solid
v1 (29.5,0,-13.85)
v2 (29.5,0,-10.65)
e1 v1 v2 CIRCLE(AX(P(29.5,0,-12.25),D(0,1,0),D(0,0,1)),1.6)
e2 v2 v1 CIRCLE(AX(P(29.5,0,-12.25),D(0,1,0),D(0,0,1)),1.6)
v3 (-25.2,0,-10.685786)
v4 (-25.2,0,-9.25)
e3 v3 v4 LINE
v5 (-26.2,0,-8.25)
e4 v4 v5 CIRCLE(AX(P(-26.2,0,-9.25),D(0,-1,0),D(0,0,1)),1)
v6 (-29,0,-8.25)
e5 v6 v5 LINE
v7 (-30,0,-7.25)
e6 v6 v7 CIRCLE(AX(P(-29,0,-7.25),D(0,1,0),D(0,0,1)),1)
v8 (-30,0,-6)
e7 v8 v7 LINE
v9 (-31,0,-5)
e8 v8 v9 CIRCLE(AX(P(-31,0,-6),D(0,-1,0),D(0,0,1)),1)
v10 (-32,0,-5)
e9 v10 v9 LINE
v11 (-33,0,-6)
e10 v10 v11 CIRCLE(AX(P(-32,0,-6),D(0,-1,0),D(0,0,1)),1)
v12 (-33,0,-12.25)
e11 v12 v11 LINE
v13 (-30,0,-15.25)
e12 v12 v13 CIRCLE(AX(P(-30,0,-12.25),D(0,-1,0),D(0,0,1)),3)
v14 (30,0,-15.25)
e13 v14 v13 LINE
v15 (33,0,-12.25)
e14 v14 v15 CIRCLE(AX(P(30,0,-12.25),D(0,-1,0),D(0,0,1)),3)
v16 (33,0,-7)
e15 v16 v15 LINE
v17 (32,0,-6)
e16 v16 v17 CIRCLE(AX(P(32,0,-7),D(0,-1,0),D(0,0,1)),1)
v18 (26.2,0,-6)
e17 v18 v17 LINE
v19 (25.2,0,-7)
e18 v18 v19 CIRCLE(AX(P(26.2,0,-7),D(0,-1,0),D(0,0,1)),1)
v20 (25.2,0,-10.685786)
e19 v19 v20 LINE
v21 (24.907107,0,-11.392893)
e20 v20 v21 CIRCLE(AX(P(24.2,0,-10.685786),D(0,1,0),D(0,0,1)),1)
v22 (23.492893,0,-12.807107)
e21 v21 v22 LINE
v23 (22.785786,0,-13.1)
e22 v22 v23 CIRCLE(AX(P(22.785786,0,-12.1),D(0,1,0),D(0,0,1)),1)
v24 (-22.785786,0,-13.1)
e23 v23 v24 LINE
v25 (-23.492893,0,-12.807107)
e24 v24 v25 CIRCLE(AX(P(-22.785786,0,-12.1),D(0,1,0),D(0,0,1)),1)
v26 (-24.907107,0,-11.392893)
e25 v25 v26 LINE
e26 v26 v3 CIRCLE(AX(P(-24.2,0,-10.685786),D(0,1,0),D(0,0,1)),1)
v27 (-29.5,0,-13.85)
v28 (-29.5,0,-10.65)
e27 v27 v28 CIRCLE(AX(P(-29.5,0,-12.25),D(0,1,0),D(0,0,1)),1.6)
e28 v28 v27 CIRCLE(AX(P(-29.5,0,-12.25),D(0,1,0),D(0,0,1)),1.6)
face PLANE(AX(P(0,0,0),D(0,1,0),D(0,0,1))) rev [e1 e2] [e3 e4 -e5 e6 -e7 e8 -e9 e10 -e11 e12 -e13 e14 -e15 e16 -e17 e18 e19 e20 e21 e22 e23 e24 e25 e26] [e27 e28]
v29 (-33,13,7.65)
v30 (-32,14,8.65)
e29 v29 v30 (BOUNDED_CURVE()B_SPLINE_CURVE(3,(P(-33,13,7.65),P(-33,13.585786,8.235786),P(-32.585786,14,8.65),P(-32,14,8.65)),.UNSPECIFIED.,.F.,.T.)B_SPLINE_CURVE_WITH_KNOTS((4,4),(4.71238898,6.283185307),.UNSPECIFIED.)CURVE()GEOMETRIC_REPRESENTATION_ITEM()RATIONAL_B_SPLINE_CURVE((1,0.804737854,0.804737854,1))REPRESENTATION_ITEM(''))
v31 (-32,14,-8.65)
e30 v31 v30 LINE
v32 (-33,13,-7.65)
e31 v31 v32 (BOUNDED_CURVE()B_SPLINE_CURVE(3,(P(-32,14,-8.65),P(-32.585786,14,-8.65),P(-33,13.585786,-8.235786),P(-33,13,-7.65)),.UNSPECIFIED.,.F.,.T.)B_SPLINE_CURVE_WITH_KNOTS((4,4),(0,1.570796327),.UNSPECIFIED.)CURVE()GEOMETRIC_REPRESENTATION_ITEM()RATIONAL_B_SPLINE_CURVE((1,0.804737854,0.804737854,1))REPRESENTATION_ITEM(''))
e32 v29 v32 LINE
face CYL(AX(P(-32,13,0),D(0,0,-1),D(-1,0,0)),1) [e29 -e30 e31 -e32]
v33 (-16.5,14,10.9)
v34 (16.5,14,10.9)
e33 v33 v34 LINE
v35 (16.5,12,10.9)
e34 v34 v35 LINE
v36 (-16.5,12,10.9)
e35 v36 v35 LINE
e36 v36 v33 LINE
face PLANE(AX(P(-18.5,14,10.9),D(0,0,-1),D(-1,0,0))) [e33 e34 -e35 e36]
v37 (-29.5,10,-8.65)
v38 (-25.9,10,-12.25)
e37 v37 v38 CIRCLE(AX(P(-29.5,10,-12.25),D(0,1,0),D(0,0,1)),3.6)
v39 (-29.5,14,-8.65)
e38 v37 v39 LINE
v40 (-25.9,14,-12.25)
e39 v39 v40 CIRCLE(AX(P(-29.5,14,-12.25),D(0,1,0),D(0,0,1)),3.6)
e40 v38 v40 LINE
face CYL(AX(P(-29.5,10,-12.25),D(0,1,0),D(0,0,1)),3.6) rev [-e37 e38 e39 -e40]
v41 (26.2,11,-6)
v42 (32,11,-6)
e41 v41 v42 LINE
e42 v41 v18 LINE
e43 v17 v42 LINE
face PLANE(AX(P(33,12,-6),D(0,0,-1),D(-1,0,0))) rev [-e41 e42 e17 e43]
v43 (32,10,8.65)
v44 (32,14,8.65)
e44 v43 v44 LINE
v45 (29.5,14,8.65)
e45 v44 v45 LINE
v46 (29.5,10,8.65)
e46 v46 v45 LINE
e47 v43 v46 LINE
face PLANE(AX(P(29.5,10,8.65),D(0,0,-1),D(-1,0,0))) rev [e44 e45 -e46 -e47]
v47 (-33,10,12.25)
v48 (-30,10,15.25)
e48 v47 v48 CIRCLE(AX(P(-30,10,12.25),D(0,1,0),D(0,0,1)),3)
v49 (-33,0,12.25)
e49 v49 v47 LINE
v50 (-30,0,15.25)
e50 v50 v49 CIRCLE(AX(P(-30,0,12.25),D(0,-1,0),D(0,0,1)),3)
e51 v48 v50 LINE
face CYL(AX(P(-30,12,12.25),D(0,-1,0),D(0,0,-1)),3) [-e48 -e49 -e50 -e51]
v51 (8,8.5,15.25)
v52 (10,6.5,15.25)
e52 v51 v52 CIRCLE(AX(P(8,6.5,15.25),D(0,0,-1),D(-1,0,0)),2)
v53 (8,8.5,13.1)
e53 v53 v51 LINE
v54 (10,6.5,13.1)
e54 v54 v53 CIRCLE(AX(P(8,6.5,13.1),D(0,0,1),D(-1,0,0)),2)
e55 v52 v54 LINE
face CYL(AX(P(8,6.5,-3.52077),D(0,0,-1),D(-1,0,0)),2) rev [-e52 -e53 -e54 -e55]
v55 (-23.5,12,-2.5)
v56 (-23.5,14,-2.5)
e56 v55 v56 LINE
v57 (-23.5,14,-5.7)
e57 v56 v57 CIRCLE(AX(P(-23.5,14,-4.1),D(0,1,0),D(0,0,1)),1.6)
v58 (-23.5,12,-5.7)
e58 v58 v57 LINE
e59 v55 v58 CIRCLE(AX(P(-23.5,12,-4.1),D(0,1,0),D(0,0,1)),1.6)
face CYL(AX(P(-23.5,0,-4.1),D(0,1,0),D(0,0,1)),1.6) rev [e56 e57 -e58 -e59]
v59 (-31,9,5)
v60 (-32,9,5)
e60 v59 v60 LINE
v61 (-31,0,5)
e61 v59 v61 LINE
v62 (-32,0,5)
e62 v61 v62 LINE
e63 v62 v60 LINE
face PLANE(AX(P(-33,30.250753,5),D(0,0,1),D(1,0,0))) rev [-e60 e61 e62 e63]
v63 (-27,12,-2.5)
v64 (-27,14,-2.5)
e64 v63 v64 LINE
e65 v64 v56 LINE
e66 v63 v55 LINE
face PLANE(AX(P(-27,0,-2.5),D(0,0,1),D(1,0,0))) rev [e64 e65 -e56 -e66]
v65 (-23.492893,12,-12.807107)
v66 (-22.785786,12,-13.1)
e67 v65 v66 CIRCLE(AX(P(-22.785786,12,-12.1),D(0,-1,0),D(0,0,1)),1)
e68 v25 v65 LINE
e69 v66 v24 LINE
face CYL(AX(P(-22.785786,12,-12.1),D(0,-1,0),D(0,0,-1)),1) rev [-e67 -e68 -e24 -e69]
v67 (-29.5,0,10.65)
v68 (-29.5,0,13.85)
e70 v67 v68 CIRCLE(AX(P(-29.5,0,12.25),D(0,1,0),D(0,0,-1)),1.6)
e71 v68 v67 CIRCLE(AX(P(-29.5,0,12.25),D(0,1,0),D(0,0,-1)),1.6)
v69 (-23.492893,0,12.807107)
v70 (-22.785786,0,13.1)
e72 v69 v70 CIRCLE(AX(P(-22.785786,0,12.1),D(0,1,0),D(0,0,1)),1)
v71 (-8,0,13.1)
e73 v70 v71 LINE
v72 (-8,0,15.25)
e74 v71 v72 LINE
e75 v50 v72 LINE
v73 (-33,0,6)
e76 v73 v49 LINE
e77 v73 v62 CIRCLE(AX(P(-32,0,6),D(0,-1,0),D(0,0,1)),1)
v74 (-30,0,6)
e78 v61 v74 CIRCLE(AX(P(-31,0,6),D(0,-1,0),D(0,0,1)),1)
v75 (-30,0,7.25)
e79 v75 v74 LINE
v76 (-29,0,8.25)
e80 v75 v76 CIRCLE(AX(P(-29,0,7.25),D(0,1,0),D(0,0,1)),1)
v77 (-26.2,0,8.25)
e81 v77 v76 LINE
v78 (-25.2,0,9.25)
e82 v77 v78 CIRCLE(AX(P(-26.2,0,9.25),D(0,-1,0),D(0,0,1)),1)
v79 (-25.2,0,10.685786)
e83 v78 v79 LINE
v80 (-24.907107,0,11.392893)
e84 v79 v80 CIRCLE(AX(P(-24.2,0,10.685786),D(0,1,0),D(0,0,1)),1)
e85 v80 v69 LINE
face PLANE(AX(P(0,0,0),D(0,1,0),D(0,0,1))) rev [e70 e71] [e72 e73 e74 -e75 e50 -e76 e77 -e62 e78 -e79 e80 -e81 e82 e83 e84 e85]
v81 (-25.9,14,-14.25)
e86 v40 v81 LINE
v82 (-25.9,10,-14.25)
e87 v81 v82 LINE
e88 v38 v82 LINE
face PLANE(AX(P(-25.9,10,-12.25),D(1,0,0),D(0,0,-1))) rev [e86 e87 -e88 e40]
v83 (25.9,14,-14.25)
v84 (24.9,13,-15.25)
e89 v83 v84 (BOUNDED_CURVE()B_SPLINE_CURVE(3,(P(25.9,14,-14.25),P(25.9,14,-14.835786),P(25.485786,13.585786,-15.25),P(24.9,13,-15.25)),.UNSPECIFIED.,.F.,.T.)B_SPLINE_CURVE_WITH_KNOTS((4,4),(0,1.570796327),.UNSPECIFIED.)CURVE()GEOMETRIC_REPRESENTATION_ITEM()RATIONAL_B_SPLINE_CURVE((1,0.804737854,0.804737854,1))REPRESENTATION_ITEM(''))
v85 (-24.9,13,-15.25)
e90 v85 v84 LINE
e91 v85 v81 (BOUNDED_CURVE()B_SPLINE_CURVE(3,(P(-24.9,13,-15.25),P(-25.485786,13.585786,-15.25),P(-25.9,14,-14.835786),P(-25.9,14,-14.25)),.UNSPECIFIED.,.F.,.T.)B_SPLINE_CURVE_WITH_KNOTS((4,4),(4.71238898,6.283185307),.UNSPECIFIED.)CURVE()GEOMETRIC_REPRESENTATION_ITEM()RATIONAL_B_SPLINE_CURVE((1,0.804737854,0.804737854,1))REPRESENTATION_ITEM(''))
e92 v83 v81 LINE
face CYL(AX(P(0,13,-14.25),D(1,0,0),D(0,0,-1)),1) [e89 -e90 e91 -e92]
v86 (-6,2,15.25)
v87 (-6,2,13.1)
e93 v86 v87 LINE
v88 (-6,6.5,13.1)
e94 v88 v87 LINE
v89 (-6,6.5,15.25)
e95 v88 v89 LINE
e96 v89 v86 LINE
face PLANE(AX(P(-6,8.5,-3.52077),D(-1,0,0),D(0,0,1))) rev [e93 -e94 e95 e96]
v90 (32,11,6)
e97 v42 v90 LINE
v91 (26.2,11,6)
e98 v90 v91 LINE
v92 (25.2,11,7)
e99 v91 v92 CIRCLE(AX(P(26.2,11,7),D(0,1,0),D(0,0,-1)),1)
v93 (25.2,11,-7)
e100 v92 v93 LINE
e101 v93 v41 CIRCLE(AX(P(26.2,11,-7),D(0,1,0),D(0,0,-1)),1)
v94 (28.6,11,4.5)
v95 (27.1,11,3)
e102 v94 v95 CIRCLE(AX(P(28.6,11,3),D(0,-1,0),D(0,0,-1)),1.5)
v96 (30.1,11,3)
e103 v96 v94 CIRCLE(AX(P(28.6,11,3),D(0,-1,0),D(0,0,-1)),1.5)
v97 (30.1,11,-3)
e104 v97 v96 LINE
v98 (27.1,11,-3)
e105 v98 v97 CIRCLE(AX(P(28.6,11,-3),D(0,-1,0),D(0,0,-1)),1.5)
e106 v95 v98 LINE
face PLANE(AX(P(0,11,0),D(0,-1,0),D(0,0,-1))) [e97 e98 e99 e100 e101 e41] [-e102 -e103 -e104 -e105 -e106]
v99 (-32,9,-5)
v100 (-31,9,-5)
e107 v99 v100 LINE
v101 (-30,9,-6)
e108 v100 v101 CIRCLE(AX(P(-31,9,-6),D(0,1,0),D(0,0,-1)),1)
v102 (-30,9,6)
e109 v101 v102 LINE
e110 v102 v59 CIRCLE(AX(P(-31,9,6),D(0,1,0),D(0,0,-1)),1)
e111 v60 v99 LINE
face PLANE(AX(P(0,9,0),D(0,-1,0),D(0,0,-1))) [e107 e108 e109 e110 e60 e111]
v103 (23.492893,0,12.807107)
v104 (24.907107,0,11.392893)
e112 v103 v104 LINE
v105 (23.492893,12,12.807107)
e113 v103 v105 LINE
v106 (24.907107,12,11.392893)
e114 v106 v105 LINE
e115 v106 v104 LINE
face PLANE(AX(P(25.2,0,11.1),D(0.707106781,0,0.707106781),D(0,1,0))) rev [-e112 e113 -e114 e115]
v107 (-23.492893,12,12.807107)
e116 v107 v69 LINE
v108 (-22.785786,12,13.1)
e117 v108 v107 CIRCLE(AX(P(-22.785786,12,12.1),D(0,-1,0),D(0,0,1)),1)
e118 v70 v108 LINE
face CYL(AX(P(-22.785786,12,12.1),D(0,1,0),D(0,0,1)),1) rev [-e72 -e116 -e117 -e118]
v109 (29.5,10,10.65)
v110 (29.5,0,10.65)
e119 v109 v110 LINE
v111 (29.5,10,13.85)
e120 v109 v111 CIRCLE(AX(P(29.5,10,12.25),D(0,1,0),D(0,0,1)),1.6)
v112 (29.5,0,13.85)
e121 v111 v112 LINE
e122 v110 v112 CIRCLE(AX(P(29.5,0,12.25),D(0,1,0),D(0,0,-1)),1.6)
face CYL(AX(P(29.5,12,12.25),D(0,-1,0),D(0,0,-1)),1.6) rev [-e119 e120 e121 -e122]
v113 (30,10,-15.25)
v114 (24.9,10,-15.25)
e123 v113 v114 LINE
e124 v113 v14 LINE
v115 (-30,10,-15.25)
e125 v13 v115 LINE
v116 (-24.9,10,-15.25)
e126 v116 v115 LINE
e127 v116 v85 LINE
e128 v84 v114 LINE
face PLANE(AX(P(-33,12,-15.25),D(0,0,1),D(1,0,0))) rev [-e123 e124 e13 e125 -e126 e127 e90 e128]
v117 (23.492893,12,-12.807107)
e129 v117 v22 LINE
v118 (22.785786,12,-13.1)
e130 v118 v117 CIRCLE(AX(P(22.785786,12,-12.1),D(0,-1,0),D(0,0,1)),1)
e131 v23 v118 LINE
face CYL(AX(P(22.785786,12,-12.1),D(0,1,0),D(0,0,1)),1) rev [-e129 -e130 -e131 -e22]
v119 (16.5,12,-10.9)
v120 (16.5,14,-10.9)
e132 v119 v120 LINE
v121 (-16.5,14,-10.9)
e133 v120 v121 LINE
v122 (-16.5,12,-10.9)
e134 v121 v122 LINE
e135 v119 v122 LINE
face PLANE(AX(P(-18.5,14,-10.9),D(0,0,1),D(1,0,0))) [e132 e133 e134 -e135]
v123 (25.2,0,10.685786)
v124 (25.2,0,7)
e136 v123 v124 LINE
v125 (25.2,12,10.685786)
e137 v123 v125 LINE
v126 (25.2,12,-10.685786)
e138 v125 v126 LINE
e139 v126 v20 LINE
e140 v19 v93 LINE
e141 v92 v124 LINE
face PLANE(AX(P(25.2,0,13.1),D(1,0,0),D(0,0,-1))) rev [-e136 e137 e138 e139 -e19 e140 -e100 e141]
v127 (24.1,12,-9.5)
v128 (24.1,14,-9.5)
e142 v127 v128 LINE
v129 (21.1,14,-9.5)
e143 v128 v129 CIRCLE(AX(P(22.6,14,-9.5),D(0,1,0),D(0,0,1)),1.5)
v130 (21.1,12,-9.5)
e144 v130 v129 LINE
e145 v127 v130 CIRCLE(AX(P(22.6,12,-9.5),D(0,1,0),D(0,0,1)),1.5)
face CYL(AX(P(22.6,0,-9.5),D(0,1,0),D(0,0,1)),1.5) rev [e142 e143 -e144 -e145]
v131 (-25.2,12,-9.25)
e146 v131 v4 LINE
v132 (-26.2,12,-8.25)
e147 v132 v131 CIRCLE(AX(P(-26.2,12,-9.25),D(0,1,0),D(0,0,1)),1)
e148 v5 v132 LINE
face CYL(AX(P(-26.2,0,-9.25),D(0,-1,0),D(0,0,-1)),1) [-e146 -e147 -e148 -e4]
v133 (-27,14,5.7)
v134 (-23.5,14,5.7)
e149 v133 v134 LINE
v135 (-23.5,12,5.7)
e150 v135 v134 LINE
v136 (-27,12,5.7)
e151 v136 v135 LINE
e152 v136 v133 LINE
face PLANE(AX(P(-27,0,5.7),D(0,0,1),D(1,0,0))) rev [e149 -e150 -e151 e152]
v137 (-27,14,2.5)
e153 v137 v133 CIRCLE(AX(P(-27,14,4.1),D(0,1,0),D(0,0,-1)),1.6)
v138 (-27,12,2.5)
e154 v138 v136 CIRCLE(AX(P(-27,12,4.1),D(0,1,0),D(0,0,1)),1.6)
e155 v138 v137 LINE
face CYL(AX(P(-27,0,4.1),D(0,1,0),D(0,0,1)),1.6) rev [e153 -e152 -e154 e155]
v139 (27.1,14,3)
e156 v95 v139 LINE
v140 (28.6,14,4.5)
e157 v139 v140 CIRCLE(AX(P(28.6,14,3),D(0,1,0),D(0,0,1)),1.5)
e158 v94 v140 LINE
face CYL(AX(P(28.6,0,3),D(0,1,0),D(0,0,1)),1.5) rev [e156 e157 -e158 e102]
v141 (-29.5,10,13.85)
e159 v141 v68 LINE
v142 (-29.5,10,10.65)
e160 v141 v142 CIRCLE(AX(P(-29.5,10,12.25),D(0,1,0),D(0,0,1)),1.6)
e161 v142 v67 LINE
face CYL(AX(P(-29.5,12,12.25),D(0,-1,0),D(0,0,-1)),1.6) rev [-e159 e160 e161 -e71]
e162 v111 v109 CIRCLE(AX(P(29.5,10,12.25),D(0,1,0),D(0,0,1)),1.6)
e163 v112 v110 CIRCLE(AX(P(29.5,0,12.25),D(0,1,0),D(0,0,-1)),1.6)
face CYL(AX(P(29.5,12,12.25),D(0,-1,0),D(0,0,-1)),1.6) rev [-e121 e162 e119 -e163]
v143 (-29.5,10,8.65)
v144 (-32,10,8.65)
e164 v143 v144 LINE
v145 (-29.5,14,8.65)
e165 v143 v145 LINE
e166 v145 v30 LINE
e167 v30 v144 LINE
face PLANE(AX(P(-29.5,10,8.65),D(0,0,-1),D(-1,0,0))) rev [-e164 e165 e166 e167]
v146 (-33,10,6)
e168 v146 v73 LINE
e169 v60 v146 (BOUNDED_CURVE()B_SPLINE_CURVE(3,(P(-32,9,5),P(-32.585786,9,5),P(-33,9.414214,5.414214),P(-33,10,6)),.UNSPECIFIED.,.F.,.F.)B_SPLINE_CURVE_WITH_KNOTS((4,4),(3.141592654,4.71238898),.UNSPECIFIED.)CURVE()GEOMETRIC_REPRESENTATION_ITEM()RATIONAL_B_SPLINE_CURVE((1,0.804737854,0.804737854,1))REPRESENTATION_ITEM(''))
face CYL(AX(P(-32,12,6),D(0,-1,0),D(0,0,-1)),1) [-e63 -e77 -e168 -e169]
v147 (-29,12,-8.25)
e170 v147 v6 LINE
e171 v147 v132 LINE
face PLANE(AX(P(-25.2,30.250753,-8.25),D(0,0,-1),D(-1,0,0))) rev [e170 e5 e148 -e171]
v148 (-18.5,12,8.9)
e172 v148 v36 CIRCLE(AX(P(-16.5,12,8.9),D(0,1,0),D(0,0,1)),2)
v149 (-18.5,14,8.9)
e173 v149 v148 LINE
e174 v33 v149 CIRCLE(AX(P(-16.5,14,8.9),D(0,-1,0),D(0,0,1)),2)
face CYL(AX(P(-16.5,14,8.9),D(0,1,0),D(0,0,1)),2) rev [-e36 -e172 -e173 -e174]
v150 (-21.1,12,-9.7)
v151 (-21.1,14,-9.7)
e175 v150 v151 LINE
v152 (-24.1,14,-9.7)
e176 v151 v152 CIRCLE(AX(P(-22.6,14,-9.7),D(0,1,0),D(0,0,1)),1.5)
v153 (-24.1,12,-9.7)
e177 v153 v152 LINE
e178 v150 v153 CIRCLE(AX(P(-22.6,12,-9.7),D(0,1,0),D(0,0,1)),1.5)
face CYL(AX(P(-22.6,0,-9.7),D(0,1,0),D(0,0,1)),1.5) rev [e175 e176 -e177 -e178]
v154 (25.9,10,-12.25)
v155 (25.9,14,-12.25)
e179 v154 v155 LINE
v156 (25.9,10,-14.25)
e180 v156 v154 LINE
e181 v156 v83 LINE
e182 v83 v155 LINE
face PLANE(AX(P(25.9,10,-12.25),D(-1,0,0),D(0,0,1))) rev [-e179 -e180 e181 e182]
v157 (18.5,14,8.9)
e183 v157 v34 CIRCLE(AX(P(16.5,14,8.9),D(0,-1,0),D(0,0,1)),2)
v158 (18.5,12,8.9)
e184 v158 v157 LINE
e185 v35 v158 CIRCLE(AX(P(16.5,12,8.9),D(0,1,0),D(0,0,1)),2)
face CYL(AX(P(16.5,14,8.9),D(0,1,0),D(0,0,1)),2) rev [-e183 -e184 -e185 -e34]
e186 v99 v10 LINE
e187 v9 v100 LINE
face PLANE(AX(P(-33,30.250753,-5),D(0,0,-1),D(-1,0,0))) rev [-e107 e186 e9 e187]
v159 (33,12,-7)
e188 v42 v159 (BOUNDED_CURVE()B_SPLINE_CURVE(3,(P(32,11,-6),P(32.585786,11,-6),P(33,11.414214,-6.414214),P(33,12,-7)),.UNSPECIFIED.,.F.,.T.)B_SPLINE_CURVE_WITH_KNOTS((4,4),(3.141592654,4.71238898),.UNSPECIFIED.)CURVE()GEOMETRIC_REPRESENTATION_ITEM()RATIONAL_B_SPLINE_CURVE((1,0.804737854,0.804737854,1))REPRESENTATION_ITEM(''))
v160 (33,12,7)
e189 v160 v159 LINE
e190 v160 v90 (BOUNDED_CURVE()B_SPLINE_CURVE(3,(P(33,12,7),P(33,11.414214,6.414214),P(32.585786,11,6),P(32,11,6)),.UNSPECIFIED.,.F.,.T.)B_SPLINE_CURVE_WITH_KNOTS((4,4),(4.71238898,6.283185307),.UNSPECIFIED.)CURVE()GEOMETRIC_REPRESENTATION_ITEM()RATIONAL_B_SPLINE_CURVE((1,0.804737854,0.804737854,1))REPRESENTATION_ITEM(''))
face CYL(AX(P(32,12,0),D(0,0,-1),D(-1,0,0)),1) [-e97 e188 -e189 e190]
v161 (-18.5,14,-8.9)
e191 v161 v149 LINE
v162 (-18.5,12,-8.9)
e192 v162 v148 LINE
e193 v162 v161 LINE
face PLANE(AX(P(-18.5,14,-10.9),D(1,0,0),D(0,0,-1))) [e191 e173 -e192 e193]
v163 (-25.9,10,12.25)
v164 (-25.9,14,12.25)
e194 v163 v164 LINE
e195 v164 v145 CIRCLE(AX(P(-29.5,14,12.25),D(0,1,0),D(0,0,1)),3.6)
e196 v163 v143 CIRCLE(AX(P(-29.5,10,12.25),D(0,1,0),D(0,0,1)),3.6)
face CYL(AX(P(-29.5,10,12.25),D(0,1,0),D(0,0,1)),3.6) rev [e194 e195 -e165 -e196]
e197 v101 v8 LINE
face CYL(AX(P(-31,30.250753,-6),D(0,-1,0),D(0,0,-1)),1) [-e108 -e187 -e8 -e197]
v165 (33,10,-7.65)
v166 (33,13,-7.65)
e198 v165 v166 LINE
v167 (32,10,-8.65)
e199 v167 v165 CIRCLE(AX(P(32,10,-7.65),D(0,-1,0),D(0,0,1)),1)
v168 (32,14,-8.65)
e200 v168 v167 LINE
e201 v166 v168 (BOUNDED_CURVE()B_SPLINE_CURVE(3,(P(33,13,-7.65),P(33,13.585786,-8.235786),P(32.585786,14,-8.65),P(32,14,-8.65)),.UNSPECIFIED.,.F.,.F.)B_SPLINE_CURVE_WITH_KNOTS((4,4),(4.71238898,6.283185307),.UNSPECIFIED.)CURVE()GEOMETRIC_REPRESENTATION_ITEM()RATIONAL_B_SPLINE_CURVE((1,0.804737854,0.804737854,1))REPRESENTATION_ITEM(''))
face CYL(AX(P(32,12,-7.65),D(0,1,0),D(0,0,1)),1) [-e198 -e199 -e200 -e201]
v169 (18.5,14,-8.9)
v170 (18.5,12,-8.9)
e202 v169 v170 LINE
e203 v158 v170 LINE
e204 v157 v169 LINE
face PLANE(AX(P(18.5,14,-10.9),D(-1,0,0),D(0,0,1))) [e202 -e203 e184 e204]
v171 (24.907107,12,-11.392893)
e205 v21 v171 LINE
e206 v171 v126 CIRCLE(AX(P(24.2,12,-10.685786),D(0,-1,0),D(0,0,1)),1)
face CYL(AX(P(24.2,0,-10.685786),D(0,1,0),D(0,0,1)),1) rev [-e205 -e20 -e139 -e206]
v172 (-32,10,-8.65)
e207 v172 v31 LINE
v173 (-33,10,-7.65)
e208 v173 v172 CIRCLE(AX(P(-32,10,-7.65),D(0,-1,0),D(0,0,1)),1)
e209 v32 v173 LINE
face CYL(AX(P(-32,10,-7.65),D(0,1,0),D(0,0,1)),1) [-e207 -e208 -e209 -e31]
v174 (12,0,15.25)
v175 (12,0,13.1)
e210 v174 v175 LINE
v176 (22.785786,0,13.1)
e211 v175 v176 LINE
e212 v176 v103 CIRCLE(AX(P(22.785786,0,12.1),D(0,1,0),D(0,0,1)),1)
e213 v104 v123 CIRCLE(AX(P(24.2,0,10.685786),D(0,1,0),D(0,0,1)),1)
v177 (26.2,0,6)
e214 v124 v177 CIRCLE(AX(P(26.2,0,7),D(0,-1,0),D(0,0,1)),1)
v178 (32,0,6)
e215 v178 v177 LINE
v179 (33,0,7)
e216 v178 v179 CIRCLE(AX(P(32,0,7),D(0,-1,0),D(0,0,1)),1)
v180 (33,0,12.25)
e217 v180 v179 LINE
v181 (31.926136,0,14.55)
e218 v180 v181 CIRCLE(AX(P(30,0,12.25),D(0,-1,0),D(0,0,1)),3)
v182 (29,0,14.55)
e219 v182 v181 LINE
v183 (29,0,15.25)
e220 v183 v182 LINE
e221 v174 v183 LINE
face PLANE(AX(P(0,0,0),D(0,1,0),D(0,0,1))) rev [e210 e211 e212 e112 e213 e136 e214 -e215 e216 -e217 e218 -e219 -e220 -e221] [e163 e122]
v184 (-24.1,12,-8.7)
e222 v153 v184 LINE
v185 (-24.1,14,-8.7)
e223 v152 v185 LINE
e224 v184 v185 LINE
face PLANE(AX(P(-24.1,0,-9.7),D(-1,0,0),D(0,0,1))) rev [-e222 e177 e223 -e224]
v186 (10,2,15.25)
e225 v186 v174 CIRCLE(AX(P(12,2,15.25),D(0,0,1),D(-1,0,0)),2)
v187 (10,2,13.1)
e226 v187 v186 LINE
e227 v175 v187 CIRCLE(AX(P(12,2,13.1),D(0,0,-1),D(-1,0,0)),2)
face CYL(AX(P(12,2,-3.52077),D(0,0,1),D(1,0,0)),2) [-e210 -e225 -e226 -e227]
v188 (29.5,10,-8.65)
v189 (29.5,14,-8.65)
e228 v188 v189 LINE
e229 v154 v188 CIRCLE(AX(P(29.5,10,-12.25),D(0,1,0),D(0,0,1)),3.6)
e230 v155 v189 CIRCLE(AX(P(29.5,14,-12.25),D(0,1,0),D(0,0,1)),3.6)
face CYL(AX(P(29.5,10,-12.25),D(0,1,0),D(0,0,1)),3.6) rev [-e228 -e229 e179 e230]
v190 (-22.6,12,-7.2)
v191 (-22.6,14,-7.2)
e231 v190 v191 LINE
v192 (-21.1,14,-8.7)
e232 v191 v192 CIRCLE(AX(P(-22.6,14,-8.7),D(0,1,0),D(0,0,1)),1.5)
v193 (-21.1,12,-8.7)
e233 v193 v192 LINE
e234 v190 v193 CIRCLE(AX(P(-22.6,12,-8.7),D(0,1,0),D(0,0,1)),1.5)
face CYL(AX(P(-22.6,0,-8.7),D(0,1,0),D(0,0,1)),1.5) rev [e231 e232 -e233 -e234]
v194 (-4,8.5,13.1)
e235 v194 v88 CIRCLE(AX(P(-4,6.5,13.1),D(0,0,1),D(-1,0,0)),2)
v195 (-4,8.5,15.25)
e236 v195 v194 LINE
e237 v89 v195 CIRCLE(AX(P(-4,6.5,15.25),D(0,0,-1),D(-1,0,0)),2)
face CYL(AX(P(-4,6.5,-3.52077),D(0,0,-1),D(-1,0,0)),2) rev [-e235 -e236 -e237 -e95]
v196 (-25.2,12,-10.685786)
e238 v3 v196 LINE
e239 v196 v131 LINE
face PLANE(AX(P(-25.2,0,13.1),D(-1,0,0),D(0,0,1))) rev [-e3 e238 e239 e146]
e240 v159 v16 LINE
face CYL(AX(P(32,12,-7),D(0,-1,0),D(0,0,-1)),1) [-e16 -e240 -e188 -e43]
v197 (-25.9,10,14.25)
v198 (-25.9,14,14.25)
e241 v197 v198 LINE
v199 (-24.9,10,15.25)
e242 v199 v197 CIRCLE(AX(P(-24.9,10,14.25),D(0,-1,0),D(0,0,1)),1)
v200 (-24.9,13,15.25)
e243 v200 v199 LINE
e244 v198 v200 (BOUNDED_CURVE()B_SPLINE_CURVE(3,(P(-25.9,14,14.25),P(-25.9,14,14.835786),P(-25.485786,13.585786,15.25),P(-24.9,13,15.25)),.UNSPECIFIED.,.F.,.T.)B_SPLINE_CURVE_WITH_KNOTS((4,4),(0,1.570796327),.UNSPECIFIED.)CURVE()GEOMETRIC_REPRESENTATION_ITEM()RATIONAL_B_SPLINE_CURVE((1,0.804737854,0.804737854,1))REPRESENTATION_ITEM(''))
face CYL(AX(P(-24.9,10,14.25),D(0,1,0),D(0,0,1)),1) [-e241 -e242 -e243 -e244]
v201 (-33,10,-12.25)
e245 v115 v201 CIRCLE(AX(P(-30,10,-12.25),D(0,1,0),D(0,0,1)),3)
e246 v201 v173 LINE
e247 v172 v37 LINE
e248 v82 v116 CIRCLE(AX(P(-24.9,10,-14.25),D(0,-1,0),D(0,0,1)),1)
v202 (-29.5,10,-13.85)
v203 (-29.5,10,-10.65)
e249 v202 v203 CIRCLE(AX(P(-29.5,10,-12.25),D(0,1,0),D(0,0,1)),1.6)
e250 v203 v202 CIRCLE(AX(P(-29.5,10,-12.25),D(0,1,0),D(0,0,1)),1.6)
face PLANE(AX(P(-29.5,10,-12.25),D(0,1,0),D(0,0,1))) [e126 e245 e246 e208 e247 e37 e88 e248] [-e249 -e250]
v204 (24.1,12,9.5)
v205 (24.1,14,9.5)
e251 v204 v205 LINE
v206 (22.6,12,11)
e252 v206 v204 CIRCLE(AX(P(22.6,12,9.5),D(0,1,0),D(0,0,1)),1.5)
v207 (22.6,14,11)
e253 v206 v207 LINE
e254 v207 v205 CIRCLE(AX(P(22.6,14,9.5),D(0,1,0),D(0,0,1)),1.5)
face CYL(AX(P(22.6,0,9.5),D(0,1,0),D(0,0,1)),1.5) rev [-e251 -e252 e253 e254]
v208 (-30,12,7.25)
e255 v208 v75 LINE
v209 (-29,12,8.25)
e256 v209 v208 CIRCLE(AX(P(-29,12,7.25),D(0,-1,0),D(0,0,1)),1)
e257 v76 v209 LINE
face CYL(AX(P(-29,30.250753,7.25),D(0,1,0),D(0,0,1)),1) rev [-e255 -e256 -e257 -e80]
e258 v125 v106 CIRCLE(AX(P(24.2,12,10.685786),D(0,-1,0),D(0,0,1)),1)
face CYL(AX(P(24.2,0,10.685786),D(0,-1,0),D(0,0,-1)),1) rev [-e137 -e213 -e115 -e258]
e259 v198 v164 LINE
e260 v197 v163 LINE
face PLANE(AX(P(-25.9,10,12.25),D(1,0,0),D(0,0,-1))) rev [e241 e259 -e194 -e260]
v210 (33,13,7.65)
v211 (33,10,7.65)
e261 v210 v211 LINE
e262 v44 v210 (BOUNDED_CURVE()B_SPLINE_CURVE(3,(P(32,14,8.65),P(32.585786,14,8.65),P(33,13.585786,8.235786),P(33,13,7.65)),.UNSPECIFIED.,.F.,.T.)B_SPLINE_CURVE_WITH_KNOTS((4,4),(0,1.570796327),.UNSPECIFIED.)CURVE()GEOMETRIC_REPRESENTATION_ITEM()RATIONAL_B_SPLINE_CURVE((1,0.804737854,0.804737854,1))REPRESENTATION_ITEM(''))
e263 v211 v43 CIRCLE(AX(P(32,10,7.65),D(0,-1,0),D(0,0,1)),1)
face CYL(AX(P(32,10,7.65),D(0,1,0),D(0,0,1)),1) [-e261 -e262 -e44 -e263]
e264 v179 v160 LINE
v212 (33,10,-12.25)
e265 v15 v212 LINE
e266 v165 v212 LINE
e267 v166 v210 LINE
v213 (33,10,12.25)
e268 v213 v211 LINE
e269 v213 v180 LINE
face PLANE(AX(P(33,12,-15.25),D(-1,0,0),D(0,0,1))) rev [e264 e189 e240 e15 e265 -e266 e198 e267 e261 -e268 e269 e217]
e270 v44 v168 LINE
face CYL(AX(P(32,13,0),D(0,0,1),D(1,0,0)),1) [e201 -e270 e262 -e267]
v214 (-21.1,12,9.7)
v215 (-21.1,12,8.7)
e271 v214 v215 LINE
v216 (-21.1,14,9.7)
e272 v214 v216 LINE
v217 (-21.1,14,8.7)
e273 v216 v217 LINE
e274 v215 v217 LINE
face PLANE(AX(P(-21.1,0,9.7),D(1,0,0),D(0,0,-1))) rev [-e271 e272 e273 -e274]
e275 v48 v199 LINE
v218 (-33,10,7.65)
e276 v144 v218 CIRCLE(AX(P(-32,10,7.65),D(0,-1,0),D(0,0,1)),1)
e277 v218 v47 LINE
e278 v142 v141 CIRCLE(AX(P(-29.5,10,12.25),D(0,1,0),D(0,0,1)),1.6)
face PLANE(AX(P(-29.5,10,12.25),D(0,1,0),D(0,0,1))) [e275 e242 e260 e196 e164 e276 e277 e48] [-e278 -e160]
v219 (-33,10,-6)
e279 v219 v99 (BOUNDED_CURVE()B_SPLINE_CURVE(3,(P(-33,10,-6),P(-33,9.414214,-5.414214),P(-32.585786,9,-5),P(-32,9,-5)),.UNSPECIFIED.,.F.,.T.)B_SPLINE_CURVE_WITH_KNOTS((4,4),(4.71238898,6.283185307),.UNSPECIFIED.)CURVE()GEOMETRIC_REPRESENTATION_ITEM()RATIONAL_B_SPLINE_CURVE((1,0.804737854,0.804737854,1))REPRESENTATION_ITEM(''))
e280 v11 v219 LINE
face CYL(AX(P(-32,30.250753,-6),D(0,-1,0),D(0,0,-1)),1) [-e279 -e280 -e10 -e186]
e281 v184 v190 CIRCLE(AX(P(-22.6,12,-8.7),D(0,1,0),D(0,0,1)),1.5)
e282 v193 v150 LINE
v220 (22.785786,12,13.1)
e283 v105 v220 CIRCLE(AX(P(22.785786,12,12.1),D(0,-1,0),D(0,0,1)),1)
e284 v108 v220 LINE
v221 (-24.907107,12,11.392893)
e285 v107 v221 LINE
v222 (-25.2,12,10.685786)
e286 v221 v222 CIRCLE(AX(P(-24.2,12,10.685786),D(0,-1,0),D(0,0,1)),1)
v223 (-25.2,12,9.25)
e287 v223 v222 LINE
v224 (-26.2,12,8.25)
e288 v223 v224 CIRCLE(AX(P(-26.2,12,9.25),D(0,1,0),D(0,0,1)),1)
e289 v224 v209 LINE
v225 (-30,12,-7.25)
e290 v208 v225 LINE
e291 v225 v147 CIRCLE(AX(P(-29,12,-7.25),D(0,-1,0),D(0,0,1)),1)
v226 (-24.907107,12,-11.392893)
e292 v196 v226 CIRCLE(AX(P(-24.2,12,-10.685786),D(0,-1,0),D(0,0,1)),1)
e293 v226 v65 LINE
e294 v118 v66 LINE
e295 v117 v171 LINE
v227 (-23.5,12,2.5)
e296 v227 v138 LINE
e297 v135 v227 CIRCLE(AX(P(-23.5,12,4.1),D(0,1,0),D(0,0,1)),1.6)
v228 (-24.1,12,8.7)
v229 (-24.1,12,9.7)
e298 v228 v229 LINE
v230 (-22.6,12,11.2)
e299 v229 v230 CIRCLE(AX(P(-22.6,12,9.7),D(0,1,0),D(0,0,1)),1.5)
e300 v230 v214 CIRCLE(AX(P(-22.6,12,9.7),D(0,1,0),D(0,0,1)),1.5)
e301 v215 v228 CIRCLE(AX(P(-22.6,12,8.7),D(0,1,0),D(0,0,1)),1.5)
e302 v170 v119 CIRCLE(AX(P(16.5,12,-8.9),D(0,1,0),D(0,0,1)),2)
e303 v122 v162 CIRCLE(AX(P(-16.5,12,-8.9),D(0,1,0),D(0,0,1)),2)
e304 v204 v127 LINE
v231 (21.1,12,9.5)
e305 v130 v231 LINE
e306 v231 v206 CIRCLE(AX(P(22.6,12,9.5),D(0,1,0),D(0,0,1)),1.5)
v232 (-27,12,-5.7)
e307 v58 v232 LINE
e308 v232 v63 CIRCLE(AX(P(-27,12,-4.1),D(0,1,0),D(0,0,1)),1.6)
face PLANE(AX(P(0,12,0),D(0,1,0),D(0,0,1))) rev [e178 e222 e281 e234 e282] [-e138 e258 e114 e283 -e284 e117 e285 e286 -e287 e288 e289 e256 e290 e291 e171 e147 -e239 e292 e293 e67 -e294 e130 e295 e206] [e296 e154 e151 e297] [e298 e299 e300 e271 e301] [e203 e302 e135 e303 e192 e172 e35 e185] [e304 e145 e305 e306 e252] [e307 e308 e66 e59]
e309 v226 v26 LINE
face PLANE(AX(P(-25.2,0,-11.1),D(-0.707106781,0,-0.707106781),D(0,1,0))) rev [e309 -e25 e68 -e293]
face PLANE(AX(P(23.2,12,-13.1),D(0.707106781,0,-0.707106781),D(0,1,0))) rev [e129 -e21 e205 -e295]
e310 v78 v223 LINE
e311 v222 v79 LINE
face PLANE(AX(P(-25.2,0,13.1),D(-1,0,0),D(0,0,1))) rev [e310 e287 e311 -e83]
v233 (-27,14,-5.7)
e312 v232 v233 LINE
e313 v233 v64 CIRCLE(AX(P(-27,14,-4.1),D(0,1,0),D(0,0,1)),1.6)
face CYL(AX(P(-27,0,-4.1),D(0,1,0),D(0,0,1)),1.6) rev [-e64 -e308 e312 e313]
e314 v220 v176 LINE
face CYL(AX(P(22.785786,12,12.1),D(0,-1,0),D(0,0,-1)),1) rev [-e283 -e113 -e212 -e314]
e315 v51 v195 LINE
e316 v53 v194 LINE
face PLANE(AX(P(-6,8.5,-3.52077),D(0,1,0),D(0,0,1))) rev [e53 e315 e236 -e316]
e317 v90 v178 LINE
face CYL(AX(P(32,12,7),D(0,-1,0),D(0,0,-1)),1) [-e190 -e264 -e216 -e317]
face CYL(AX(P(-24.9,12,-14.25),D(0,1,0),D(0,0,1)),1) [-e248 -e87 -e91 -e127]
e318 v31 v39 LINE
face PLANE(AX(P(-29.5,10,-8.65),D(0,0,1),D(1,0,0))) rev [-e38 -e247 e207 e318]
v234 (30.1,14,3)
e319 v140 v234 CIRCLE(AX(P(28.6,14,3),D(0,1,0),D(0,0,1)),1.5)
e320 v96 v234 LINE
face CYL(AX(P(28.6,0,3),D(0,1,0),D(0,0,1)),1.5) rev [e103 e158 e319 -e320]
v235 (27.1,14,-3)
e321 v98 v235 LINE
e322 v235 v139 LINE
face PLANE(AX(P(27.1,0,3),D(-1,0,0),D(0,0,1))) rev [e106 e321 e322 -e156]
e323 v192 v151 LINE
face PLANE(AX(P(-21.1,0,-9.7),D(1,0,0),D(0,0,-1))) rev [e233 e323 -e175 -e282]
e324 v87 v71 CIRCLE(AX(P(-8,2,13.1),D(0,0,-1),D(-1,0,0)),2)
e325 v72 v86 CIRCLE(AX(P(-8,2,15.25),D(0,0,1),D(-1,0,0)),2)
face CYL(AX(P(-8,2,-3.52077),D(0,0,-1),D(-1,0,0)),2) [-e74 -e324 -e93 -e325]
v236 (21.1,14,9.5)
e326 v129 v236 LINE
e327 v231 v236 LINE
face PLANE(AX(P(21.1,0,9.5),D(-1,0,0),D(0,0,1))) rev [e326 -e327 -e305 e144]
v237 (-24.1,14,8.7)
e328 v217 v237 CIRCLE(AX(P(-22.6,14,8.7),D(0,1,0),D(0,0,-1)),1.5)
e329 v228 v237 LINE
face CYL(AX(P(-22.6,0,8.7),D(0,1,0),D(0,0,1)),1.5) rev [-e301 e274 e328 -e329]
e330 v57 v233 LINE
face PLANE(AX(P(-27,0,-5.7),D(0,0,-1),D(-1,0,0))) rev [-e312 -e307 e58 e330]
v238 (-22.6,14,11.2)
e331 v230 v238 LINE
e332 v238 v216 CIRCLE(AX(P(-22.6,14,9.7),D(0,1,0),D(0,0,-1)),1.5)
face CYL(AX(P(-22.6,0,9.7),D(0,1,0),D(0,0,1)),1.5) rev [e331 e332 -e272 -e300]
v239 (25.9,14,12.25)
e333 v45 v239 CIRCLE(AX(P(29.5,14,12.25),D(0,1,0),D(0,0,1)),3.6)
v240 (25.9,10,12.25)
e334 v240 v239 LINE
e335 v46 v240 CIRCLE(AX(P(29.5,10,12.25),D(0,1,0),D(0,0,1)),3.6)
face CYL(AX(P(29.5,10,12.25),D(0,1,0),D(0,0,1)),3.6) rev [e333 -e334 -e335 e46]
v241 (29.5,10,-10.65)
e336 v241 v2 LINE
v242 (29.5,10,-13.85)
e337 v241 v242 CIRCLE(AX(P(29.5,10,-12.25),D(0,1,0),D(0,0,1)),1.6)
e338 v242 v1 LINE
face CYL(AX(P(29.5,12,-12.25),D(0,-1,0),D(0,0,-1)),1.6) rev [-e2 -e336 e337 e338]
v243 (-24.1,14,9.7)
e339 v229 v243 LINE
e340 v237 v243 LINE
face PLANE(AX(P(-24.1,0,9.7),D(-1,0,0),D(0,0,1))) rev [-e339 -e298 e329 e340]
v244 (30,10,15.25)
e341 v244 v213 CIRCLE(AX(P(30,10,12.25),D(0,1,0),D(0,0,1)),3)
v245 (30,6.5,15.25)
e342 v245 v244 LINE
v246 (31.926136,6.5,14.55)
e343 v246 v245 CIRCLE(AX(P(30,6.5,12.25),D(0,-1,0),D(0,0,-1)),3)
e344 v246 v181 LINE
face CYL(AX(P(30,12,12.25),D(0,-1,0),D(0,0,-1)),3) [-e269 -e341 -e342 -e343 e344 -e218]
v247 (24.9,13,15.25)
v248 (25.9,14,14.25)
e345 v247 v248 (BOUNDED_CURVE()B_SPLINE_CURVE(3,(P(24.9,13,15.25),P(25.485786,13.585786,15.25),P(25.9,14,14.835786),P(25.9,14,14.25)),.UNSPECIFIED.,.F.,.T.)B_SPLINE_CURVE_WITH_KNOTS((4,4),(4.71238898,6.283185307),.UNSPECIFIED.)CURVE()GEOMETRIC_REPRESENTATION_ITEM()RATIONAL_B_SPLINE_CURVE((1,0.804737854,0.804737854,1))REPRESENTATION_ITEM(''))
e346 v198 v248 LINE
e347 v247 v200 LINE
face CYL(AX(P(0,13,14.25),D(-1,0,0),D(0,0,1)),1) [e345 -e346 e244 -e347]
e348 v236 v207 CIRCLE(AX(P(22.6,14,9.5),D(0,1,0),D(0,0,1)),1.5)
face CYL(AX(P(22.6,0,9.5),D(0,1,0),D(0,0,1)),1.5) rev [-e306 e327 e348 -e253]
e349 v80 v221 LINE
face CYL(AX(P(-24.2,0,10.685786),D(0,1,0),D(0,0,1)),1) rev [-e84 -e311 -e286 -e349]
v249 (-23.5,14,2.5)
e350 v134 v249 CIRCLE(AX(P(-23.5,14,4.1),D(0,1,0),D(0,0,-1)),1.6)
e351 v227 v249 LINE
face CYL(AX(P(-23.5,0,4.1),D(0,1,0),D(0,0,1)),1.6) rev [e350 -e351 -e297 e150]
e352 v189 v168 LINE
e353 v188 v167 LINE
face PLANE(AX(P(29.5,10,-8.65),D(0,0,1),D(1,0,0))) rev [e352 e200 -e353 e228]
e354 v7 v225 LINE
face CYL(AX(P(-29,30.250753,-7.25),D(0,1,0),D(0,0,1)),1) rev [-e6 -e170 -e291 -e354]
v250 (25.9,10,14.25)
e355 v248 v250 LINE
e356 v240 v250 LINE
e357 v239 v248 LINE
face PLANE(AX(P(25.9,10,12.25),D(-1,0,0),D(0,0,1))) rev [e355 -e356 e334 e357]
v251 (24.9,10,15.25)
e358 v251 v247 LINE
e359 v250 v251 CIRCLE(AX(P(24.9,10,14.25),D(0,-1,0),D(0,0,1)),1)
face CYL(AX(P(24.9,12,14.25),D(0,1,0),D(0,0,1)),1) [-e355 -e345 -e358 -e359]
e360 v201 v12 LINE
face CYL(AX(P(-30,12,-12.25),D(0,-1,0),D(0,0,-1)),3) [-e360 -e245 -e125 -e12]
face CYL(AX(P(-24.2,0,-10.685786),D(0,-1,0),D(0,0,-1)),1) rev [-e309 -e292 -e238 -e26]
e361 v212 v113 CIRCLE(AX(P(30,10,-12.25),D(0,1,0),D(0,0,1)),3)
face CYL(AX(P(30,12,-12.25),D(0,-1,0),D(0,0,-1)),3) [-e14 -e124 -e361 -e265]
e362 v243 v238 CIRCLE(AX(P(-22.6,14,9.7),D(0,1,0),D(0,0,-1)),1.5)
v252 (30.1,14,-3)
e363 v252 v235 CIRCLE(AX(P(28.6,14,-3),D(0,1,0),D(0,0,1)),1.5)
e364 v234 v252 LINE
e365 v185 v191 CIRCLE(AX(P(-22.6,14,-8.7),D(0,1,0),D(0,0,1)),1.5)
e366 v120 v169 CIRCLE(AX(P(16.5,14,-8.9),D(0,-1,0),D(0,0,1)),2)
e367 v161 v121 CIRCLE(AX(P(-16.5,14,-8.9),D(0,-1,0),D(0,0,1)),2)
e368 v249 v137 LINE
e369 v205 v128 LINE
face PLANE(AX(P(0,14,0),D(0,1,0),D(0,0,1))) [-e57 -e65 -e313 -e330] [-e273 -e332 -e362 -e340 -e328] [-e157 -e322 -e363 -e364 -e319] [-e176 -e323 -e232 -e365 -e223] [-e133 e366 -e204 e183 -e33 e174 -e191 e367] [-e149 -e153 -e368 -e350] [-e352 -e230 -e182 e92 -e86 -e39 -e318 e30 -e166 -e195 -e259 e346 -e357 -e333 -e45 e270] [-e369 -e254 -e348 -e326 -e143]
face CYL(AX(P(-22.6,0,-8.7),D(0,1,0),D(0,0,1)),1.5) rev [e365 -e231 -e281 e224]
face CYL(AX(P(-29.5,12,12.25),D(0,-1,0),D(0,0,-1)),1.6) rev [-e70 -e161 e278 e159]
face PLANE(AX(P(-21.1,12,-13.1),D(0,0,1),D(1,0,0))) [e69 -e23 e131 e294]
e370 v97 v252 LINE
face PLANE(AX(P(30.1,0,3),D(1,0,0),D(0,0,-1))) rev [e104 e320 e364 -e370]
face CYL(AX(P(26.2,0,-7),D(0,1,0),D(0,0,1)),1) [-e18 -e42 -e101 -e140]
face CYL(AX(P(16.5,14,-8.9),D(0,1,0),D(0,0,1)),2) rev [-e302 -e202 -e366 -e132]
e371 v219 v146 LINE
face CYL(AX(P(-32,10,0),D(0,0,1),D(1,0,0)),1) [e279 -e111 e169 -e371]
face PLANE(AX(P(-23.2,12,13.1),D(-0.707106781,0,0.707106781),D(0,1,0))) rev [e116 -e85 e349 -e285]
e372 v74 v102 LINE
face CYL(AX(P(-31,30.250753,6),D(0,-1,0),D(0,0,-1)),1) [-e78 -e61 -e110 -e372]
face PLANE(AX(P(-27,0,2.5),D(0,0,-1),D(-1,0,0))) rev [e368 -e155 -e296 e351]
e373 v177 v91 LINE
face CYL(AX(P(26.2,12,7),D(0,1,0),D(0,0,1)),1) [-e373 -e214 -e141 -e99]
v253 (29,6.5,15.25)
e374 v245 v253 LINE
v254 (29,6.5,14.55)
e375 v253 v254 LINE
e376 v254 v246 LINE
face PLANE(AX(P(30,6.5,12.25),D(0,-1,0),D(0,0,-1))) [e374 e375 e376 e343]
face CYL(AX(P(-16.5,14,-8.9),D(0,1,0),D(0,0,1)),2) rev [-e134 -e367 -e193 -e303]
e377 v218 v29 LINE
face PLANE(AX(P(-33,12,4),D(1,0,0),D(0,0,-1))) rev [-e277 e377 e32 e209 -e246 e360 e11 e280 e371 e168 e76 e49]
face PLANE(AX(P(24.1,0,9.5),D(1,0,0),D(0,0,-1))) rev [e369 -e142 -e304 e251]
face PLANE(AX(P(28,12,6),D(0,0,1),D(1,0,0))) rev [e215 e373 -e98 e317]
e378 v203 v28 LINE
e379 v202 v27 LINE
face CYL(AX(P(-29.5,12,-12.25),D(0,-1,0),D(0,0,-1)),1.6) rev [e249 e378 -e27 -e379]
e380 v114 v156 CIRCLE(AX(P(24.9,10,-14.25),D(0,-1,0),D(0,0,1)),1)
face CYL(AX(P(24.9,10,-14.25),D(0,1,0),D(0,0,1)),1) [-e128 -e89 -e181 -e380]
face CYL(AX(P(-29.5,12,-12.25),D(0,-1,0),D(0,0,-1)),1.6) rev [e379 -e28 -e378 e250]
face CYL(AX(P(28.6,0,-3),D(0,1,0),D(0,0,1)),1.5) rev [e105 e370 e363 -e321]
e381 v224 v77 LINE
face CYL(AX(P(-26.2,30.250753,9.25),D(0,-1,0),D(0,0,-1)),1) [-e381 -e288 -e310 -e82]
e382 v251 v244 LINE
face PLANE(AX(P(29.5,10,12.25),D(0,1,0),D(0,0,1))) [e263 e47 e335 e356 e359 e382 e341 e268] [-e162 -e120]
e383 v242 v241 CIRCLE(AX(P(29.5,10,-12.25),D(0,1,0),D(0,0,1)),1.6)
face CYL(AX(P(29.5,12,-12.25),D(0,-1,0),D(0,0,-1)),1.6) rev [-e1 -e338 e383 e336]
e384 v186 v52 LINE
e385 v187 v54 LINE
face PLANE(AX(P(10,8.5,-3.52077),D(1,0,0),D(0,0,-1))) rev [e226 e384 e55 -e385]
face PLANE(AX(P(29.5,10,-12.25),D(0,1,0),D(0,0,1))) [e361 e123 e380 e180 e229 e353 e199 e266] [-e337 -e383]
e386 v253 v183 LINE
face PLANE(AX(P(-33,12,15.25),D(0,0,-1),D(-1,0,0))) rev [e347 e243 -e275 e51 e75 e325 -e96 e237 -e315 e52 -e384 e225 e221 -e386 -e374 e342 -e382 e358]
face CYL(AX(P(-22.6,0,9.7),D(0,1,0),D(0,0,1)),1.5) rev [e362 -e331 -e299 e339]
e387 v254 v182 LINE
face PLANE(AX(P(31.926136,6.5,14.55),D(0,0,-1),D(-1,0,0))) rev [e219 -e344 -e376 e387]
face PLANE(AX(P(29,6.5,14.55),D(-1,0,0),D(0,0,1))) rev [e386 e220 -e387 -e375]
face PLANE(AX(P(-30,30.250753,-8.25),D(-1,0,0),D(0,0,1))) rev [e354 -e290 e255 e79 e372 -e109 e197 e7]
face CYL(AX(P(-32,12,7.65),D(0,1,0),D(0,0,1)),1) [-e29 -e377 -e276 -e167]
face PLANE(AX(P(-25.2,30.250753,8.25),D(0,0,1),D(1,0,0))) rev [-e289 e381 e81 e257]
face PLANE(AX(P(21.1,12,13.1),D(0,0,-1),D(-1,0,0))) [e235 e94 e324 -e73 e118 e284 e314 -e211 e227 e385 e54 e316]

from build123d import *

# Parameters (mm, degrees)
SKETCH1_R              = 1.6
BOSS_EXTRUDE1_DEPTH    = 12
SKETCH2_W              = 52
SKETCH2_H              = 26.2
CUT_EXTRUDE1_DEPTH     = 2
SKETCH3_W              = 7.4
SKETCH3_H              = 20
CUT_EXTRUDE2_DEPTH     = 8
SKETCH4_W              = 16
SKETCH4_H              = 4.5
CUT_EXTRUDE3_DEPTH     = 2.15
SKETCH5_W              = 52
SKETCH5_H              = 26.2
CUT_EXTRUDE4_DEPTH     = 39.28266579
SKETCH6_W              = 66
SKETCH6_H              = 30.5
SKETCH6_R              = 1.6
SKETCH6_W_2            = 37
SKETCH6_H_2            = 21.8
BOSS_EXTRUDE2_DEPTH    = 2
SKETCH7_W              = 2
SKETCH7_H              = 12
SKETCH7_W_2            = 1.6
SKETCH7_H_2            = 8
CUT_EXTRUDE5_DEPTH     = 39.28266579
SKETCH8_W              = 16
SKETCH8_H              = 2.15
CUT_EXTRUDE6_DEPTH     = 38.33379836
SKETCH9_W              = 0.8
SKETCH9_H              = 7.1
BOSS_EXTRUDE3_DEPTH    = 12
CUT_EXTRUDE7_DEPTH     = 12
SKETCH11_W             = 3
SKETCH11_H             = 10
BOSS_EXTRUDE4_DEPTH    = 3
SKETCH13_W             = 7.8
SKETCH13_H             = 12
BOSS_EXTRUDE5_DEPTH    = 1
CHAMFER1_SIZE          = 2
CUT_EXTRUDE8_DEPTH     = 4
CUT_EXTRUDE9_DEPTH     = 39.955904559
R1_TRANSITION_FILLET_R = 1
R2_TRANSITION_FILLET_R = 2
R3_TRANSITION_FILLET_R = 3
CUT_EXTRUDE10_START    = -6.5
CUT_EXTRUDE10_DEPTH    = 6.5


with BuildPart() as part:
    # Sketch1 → Boss-Extrude1 (new body)
    with BuildSketch(Plane(origin=(0, 0, 0), x_dir=(1, 0, 0), z_dir=(0, 1, 0))):
        Polygon((-33, 4), (-27.6, 4), (-27.6, -4), (-33, -4), (-33, -15.25), (33, -15.25), (33, -6), (28, -6), (28, 6), (33, 6), (33, 15.25), (-33, 15.25), align=None)
        with Locations(Location((-29.5, 12.25, 0), (0, 0, 270))):
            Circle(SKETCH1_R, mode=Mode.SUBTRACT)
        with Locations(Location((29.5, 12.25, 0), (0, 0, 270))):
            Circle(SKETCH1_R, mode=Mode.SUBTRACT)
        with Locations(Location((-29.5, -12.25, 0), (0, 0, 90))):
            Circle(SKETCH1_R, mode=Mode.SUBTRACT)
        with Locations(Location((29.5, -12.25, 0), (0, 0, 90))):
            Circle(SKETCH1_R, mode=Mode.SUBTRACT)
        Polygon((-26, -5.75), (-26, 5.75), (-21.1, 5.75), (-21.1, 13.1), (21.1, 13.1), (21.1, -13.1), (-21.1, -13.1), (-21.1, -5.75), align=None, mode=Mode.SUBTRACT)
    extrude(amount=BOSS_EXTRUDE1_DEPTH)

    # Sketch2 → Cut-Extrude1 (cut)
    with BuildSketch(Plane.XZ):
        Rectangle(SKETCH2_W, SKETCH2_H)
    extrude(amount=-CUT_EXTRUDE1_DEPTH, mode=Mode.SUBTRACT)

    # Sketch3 → Cut-Extrude2 (cut)
    with BuildSketch(Plane(origin=(0, 12, 0), x_dir=(1, 0, 0), z_dir=(0, 1, 0))):
        with Locations((-26.8, 0)):
            Rectangle(SKETCH3_W, SKETCH3_H)
        Polygon((28, -6), (28, 6), (26, 6), (26, 13.1), (21.1, 13.1), (21.1, -13.1), (26, -13.1), (26, -6), align=None)
    extrude(amount=-CUT_EXTRUDE2_DEPTH, mode=Mode.SUBTRACT)

    # Sketch4 → Cut-Extrude3 (cut)
    with BuildSketch(Plane.XY.offset(15.25)):
        with Locations((2, 6.25)):
            Rectangle(SKETCH4_W, SKETCH4_H)
    extrude(amount=-CUT_EXTRUDE3_DEPTH, mode=Mode.SUBTRACT)

    # Sketch5 → Cut-Extrude4 (cut, through all)
    with BuildSketch(Plane.XZ):
        Rectangle(SKETCH5_W, SKETCH5_H)
    extrude(amount=-CUT_EXTRUDE4_DEPTH, mode=Mode.SUBTRACT)

    # Sketch6 → Boss-Extrude2 (add)
    with BuildSketch(Plane(origin=(0, 12, 0), x_dir=(1, 0, 0), z_dir=(0, 1, 0))):
        Rectangle(SKETCH6_W, SKETCH6_H)
        with Locations(Location((-29.5, -12.25, 0), (0, 0, 90))):
            Circle(SKETCH6_R, mode=Mode.SUBTRACT)
        with Locations(Location((29.5, -12.25, 0), (0, 0, 90))):
            Circle(SKETCH6_R, mode=Mode.SUBTRACT)
        with Locations(Location((29.5, 12.25, 0), (0, 0, 270))):
            Circle(SKETCH6_R, mode=Mode.SUBTRACT)
        with Locations(Location((-29.5, 12.25, 0), (0, 0, 270))):
            Circle(SKETCH6_R, mode=Mode.SUBTRACT)
        Rectangle(SKETCH6_W_2, SKETCH6_H_2, mode=Mode.SUBTRACT)
    extrude(amount=BOSS_EXTRUDE2_DEPTH)

    # Sketch7 → Cut-Extrude5 (cut, through all)
    with BuildSketch(Plane.XZ.offset(-12)):
        with Locations((27, 0)):
            Rectangle(SKETCH7_W, SKETCH7_H)
        with Locations((-26.8, 0)):
            Rectangle(SKETCH7_W_2, SKETCH7_H_2)
    extrude(amount=CUT_EXTRUDE5_DEPTH, mode=Mode.SUBTRACT)

    # Sketch8 → Cut-Extrude6 (cut, through all)
    with BuildSketch(Plane.XZ.offset(-8.5)):
        with Locations((2, 14.175)):
            Rectangle(SKETCH8_W, SKETCH8_H)
    extrude(amount=CUT_EXTRUDE6_DEPTH, mode=Mode.SUBTRACT)

    # Sketch9 → Boss-Extrude3 (add, through all)
    with BuildSketch(Plane.XZ.offset(-12)):
        with Locations((25.6, 9.55)):
            Rectangle(SKETCH9_W, SKETCH9_H)
        Polygon((-25.2, -13.1), (-26, -13.1), (-26, -10), (-30.5, -10), (-30.5, -4), (-33, -4), (-33, 4), (-30.5, 4), (-30.5, 10), (-26, 10), (-26, 13.1), (-25.2, 13.1), align=None)
        with Locations((25.6, -9.55)):
            Rectangle(SKETCH9_W, SKETCH9_H)
    extrude(amount=BOSS_EXTRUDE3_DEPTH)

    # Sketch10 → Cut-Extrude7 (cut)
    with BuildSketch(Plane.XZ):
        Polygon((-33, -5), (-33, 5), (-30, 5), (-30, 8.25), (-25.2, 8.25), (-25.2, -8.25), (-30, -8.25), (-30, -5), align=None)
    extrude(amount=-CUT_EXTRUDE7_DEPTH, mode=Mode.SUBTRACT)

    # Sketch11 → Boss-Extrude4 (add)
    with BuildSketch(Plane.XZ.offset(-12)):
        with Locations((-31.5, 0)):
            Rectangle(SKETCH11_W, SKETCH11_H)
    extrude(amount=BOSS_EXTRUDE4_DEPTH)

    # Sketch13 → Boss-Extrude5 (add)
    with BuildSketch(Plane.XZ.offset(-12)):
        with Locations((29.1, 0)):
            Rectangle(SKETCH13_W, SKETCH13_H)
    extrude(amount=BOSS_EXTRUDE5_DEPTH)

    # Chamfer1
    chamfer1_edges = [part.edges().sort_by_distance(p)[0] for p in [
        (-25.2, 6, -13.1),
        (-25.2, 6, 13.1),
        (25.2, 6, 13.1),
        (25.2, 6, -13.1),
    ]]
    chamfer(chamfer1_edges, length=CHAMFER1_SIZE)

    # Sketch12 → Cut-Extrude8 (cut)
    with BuildSketch(Plane(origin=(0, 14, 0), x_dir=(1, 0, 0), z_dir=(0, 1, 0))):
        with BuildLine():
            Line((-29.5, 8.65), (-33, 8.65))
            Line((-33, 8.65), (-33, 15.25))
            Line((-33, 15.25), (-25.9, 15.25))
            Line((-25.9, 15.25), (-25.9, 12.25))
            ThreePointArc((-25.9, 12.25), (-26.954415588, 9.704415588), (-29.5, 8.65))
        make_face()
        with BuildLine():
            Line((29.5, 8.65), (33, 8.65))
            Line((33, 8.65), (33, 15.25))
            Line((33, 15.25), (25.9, 15.25))
            Line((25.9, 15.25), (25.9, 12.25))
            ThreePointArc((25.9, 12.25), (26.954415588, 9.704415588), (29.5, 8.65))
        make_face()
        with BuildLine():
            Line((29.5, -8.65), (33, -8.65))
            Line((33, -8.65), (33, -15.25))
            Line((33, -15.25), (25.9, -15.25))
            Line((25.9, -15.25), (25.9, -12.25))
            ThreePointArc((25.9, -12.25), (26.954415588, -9.704415588), (29.5, -8.65))
        make_face()
        with BuildLine():
            Line((-25.9, -12.25), (-25.9, -15.25))
            Line((-25.9, -15.25), (-33, -15.25))
            Line((-33, -15.25), (-33, -8.65))
            Line((-33, -8.65), (-29.5, -8.65))
            ThreePointArc((-29.5, -8.65), (-26.954415588, -9.704415588), (-25.9, -12.25))
        make_face()
    extrude(amount=-CUT_EXTRUDE8_DEPTH, mode=Mode.SUBTRACT)

    # Sketch14 → Cut-Extrude9 (cut, through all)
    with BuildSketch(Plane(origin=(0, 14, 0), x_dir=(1, 0, 0), z_dir=(0, 1, 0))):
        with BuildLine():
            Line((21.1, -9.5), (21.1, 9.5))
            ThreePointArc((21.1, 9.5), (22.6, 11), (24.1, 9.5))
            Line((24.1, 9.5), (24.1, -9.5))
            ThreePointArc((24.1, -9.5), (22.6, -11), (21.1, -9.5))
        make_face()
        with BuildLine():
            Line((27.1, -3), (27.1, 3))
            ThreePointArc((27.1, 3), (28.6, 4.5), (30.1, 3))
            Line((30.1, 3), (30.1, -3))
            ThreePointArc((30.1, -3), (28.6, -4.5), (27.1, -3))
        make_face()
        with BuildLine():
            Line((-27, 5.7), (-23.5, 5.7))
            ThreePointArc((-23.5, 5.7), (-21.9, 4.1), (-23.5, 2.5))
            Line((-23.5, 2.5), (-27, 2.5))
            ThreePointArc((-27, 2.5), (-28.6, 4.1), (-27, 5.7))
        make_face()
        with BuildLine():
            Line((-27, -5.7), (-23.5, -5.7))
            ThreePointArc((-23.5, -5.7), (-21.9, -4.1), (-23.5, -2.5))
            Line((-23.5, -2.5), (-27, -2.5))
            ThreePointArc((-27, -2.5), (-28.6, -4.1), (-27, -5.7))
        make_face()
        with BuildLine():
            Line((-21.1, 9.7), (-21.1, 8.7))
            ThreePointArc((-21.1, 8.7), (-22.6, 7.2), (-24.1, 8.7))
            Line((-24.1, 8.7), (-24.1, 9.7))
            ThreePointArc((-24.1, 9.7), (-22.6, 11.2), (-21.1, 9.7))
        make_face()
        with BuildLine():
            Line((-21.1, -9.7), (-21.1, -8.7))
            ThreePointArc((-21.1, -8.7), (-22.6, -7.2), (-24.1, -8.7))
            Line((-24.1, -8.7), (-24.1, -9.7))
            ThreePointArc((-24.1, -9.7), (-22.6, -11.2), (-21.1, -9.7))
        make_face()
    extrude(amount=-CUT_EXTRUDE9_DEPTH, mode=Mode.SUBTRACT)

    # R1 transition fillet
    r1_transition_fillet_edges = [part.edges().sort_by_distance(p)[0] for p in [
        (25.2, 5.5, 6),
        (25.2, 5.5, -6),
        (-30, 6, -8.25),
        (-25.2, 6, -8.25),
        (-25.2, 6, 8.25),
        (-30, 6, 8.25),
        (-30, 4.5, 5),
        (-33, 4.5, 5),
        (-30, 4.5, -5),
        (-33, 4.5, -5),
        (-33, 9, 0),
        (33, 5.5, 6),
        (33, 5.5, -6),
        (33, 11, 0),
        (-25.2, 6, -11.1),
        (23.2, 6, -13.1),
        (-23.2, 6, -13.1),
        (25.2, 6, 11.1),
        (25.2, 6, -11.1),
        (-23.2, 6, 13.1),
        (23.2, 6, 13.1),
        (-25.2, 6, 11.1),
        (0, 14, -15.25),
        (-33, 14, 0),
        (0, 14, 15.25),
        (33, 14, 0),
        (33, 12, 8.65),
        (25.9, 12, 15.25),
        (-25.9, 12, 15.25),
        (-33, 12, 8.65),
        (-33, 12, -8.65),
        (-25.9, 12, -15.25),
        (25.9, 12, -15.25),
        (33, 12, -8.65),
    ]]
    fillet(r1_transition_fillet_edges, radius=R1_TRANSITION_FILLET_R)

    # R2 transition fillet
    r2_transition_fillet_edges = [part.edges().sort_by_distance(p)[0] for p in [
        (10, 8.5, 14.175),
        (-6, 8.5, 14.175),
        (-18.5, 13, 10.9),
        (18.5, 13, 10.9),
        (18.5, 13, -10.9),
        (-18.5, 13, -10.9),
        (10, 0, 14.175),
        (-6, 0, 14.175),
    ]]
    fillet(r2_transition_fillet_edges, radius=R2_TRANSITION_FILLET_R)

    # R3 transition fillet
    r3_transition_fillet_edges = [part.edges().sort_by_distance(p)[0] for p in [
        (-33, 5, 15.25),
        (-33, 5, -15.25),
        (33, 5, -15.25),
        (33, 5, 15.25),
    ]]
    fillet(r3_transition_fillet_edges, radius=R3_TRANSITION_FILLET_R)

    # Sketch15 → Cut-Extrude10 (cut)
    with BuildSketch(Plane.XZ.offset(CUT_EXTRUDE10_START)):
        with BuildLine():
            Line((29, 15.25), (30, 15.25))
            ThreePointArc((30, 15.25), (31.024695077, 15.069574436), (31.926136028, 14.55))
            Line((31.926136028, 14.55), (29, 14.55))
            Line((29, 14.55), (29, 15.25))
        make_face()
    extrude(amount=CUT_EXTRUDE10_DEPTH, mode=Mode.SUBTRACT)


solid = part.part
